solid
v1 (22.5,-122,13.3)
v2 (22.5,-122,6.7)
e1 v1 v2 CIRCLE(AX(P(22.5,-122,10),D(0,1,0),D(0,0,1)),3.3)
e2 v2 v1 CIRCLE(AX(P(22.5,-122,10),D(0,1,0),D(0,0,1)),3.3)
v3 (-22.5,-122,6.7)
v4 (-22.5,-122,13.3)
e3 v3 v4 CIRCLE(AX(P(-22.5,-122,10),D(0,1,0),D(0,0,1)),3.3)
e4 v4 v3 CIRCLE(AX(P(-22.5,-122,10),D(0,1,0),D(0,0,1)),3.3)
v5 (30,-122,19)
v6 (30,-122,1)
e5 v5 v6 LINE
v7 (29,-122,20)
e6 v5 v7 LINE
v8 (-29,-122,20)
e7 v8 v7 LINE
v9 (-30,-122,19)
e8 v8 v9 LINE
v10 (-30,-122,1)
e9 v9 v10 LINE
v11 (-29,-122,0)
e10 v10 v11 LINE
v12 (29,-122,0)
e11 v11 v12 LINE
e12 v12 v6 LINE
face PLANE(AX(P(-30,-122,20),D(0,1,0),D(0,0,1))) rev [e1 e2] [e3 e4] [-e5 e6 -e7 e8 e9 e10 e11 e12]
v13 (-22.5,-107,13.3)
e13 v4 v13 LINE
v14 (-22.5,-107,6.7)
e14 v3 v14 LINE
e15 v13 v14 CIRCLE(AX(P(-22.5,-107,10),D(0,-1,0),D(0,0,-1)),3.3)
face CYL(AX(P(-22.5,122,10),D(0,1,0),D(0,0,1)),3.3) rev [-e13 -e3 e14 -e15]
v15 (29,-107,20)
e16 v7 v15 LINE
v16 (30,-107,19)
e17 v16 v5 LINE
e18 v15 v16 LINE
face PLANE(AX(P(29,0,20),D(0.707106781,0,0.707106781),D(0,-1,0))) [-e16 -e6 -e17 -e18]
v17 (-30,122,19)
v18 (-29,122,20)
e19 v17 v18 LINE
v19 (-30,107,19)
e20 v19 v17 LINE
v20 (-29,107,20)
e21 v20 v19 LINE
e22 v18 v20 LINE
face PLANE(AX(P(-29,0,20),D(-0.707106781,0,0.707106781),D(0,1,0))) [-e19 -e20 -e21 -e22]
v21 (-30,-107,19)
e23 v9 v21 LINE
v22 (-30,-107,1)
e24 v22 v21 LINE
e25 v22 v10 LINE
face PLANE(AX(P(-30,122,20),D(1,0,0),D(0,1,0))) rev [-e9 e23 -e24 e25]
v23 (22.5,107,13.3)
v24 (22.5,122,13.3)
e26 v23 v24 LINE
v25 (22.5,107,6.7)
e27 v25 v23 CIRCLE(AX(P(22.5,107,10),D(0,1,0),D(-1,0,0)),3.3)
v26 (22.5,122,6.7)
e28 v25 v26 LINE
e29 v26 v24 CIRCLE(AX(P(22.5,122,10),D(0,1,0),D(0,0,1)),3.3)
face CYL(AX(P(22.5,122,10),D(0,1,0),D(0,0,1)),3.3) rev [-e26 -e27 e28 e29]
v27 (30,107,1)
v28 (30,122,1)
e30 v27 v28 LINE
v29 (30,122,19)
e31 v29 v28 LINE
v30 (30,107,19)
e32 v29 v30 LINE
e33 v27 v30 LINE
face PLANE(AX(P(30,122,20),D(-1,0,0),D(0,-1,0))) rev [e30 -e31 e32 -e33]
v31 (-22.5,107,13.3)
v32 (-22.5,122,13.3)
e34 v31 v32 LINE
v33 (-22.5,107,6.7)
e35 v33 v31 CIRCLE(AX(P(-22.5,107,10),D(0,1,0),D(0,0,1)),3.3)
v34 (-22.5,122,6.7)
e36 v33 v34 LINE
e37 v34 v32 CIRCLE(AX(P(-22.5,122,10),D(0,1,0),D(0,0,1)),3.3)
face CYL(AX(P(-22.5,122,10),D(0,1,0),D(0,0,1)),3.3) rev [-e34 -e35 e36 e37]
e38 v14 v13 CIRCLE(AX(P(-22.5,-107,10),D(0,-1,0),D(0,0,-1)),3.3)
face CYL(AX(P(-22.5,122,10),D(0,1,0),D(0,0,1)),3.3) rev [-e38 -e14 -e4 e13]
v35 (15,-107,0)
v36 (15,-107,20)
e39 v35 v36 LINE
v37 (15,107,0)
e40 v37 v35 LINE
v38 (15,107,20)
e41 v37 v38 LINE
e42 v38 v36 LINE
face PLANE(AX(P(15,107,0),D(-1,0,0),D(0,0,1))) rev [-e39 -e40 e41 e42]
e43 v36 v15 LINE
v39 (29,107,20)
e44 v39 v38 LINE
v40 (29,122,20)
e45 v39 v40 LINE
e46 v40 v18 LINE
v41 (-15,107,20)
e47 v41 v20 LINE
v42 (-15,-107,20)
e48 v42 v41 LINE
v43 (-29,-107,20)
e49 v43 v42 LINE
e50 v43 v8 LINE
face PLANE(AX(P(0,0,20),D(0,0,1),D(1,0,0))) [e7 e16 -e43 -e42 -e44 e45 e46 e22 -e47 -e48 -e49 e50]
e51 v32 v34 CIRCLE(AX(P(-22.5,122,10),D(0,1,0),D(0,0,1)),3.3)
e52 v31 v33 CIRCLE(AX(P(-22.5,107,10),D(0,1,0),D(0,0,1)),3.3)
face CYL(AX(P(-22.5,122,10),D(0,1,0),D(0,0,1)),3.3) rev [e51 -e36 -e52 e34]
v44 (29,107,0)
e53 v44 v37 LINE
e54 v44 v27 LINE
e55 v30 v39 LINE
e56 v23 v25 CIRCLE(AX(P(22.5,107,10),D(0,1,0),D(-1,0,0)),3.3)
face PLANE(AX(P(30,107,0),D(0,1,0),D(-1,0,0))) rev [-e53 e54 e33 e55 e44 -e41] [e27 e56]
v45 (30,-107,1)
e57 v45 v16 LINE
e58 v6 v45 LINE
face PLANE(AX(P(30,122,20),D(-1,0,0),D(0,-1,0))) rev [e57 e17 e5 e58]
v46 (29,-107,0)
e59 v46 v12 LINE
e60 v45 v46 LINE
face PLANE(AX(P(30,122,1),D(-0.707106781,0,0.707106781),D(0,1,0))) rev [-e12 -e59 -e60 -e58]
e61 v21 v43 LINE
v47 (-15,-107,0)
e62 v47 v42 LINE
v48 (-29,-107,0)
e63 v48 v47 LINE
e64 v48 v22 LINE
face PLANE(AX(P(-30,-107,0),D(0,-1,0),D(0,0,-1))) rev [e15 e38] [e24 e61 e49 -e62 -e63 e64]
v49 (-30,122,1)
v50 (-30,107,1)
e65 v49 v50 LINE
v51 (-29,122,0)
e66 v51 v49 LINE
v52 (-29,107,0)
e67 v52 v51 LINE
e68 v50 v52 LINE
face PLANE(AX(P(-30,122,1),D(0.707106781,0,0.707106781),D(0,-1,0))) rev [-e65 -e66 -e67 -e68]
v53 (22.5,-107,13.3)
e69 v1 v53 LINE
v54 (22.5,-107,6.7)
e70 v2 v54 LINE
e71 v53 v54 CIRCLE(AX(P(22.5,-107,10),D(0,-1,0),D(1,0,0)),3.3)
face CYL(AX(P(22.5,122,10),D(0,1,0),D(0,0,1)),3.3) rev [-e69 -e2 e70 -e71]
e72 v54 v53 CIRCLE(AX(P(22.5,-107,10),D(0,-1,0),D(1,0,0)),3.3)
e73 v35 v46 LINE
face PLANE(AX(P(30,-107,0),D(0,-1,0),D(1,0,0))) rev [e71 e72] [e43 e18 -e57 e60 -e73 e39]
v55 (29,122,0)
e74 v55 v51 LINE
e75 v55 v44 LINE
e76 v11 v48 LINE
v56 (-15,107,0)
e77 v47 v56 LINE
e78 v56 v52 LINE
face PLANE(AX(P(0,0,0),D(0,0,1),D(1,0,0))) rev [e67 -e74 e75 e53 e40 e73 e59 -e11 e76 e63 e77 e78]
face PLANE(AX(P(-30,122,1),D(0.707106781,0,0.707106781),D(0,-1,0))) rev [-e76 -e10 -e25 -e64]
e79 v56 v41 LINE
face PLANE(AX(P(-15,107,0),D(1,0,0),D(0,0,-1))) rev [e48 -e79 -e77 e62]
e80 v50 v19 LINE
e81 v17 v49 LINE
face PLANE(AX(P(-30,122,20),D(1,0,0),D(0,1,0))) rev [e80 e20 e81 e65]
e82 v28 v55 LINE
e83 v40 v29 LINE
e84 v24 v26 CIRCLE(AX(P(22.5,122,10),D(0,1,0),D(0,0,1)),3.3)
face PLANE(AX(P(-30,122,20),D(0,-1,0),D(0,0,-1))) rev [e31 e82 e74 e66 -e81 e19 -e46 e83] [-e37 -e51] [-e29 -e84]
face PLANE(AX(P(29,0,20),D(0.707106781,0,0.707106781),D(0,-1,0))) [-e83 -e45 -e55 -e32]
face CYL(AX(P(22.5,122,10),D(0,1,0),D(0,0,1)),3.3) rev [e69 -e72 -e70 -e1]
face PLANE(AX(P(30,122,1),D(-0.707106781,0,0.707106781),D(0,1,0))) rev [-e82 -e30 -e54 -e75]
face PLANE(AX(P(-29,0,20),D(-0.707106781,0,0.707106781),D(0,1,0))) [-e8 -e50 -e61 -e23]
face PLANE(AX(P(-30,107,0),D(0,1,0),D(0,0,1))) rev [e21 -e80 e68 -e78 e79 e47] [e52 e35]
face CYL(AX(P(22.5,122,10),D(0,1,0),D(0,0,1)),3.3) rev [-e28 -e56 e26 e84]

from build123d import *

# Parameters (mm, degrees)
SKETCH1_W            = 60
SKETCH1_H            = 244
BOSS_EXTRUDE1_DEPTH  = 20
SKETCH2_W            = 15
SKETCH2_H            = 214
CUT_EXTRUDE1_DEPTH   = 128.21635115
M6_CLEARANCE_HOLE1_D = 6.6
CHAMFER1_SIZE        = 1


with BuildPart() as part:
    # Sketch1 → Boss-Extrude1 (new body)
    with BuildSketch(Plane.XY):
        Rectangle(SKETCH1_W, SKETCH1_H)
    extrude(amount=BOSS_EXTRUDE1_DEPTH)

    # Sketch2 → Cut-Extrude1 (cut, through all)
    with BuildSketch(Plane.XY.offset(20)):
        with Locations((-22.5, 0)):
            Rectangle(SKETCH2_W, SKETCH2_H)
        with Locations((22.5, 0)):
            Rectangle(SKETCH2_W, SKETCH2_H)
    extrude(amount=-CUT_EXTRUDE1_DEPTH, mode=Mode.SUBTRACT)

    # M6 Clearance Hole1 (through all)
    with Locations(Plane(origin=(0, 122, 0), x_dir=(1, 0, 0), z_dir=(0, 1, 0))):
        with Locations((-22.5, -10), (22.5, -10)):
            Hole(M6_CLEARANCE_HOLE1_D / 2)

    # Chamfer1
    chamfer1_edges = [part.edges().sort_by_distance(p)[0] for p in [
        (-30, 114.5, 20),
        (30, 114.5, 0),
        (-30, -114.5, 0),
        (30, 114.5, 20),
        (-30, -114.5, 20),
        (30, -114.5, 20),
        (-30, 114.5, 0),
        (30, -114.5, 0),
    ]]
    chamfer(chamfer1_edges, length=CHAMFER1_SIZE)


solid = part.part
